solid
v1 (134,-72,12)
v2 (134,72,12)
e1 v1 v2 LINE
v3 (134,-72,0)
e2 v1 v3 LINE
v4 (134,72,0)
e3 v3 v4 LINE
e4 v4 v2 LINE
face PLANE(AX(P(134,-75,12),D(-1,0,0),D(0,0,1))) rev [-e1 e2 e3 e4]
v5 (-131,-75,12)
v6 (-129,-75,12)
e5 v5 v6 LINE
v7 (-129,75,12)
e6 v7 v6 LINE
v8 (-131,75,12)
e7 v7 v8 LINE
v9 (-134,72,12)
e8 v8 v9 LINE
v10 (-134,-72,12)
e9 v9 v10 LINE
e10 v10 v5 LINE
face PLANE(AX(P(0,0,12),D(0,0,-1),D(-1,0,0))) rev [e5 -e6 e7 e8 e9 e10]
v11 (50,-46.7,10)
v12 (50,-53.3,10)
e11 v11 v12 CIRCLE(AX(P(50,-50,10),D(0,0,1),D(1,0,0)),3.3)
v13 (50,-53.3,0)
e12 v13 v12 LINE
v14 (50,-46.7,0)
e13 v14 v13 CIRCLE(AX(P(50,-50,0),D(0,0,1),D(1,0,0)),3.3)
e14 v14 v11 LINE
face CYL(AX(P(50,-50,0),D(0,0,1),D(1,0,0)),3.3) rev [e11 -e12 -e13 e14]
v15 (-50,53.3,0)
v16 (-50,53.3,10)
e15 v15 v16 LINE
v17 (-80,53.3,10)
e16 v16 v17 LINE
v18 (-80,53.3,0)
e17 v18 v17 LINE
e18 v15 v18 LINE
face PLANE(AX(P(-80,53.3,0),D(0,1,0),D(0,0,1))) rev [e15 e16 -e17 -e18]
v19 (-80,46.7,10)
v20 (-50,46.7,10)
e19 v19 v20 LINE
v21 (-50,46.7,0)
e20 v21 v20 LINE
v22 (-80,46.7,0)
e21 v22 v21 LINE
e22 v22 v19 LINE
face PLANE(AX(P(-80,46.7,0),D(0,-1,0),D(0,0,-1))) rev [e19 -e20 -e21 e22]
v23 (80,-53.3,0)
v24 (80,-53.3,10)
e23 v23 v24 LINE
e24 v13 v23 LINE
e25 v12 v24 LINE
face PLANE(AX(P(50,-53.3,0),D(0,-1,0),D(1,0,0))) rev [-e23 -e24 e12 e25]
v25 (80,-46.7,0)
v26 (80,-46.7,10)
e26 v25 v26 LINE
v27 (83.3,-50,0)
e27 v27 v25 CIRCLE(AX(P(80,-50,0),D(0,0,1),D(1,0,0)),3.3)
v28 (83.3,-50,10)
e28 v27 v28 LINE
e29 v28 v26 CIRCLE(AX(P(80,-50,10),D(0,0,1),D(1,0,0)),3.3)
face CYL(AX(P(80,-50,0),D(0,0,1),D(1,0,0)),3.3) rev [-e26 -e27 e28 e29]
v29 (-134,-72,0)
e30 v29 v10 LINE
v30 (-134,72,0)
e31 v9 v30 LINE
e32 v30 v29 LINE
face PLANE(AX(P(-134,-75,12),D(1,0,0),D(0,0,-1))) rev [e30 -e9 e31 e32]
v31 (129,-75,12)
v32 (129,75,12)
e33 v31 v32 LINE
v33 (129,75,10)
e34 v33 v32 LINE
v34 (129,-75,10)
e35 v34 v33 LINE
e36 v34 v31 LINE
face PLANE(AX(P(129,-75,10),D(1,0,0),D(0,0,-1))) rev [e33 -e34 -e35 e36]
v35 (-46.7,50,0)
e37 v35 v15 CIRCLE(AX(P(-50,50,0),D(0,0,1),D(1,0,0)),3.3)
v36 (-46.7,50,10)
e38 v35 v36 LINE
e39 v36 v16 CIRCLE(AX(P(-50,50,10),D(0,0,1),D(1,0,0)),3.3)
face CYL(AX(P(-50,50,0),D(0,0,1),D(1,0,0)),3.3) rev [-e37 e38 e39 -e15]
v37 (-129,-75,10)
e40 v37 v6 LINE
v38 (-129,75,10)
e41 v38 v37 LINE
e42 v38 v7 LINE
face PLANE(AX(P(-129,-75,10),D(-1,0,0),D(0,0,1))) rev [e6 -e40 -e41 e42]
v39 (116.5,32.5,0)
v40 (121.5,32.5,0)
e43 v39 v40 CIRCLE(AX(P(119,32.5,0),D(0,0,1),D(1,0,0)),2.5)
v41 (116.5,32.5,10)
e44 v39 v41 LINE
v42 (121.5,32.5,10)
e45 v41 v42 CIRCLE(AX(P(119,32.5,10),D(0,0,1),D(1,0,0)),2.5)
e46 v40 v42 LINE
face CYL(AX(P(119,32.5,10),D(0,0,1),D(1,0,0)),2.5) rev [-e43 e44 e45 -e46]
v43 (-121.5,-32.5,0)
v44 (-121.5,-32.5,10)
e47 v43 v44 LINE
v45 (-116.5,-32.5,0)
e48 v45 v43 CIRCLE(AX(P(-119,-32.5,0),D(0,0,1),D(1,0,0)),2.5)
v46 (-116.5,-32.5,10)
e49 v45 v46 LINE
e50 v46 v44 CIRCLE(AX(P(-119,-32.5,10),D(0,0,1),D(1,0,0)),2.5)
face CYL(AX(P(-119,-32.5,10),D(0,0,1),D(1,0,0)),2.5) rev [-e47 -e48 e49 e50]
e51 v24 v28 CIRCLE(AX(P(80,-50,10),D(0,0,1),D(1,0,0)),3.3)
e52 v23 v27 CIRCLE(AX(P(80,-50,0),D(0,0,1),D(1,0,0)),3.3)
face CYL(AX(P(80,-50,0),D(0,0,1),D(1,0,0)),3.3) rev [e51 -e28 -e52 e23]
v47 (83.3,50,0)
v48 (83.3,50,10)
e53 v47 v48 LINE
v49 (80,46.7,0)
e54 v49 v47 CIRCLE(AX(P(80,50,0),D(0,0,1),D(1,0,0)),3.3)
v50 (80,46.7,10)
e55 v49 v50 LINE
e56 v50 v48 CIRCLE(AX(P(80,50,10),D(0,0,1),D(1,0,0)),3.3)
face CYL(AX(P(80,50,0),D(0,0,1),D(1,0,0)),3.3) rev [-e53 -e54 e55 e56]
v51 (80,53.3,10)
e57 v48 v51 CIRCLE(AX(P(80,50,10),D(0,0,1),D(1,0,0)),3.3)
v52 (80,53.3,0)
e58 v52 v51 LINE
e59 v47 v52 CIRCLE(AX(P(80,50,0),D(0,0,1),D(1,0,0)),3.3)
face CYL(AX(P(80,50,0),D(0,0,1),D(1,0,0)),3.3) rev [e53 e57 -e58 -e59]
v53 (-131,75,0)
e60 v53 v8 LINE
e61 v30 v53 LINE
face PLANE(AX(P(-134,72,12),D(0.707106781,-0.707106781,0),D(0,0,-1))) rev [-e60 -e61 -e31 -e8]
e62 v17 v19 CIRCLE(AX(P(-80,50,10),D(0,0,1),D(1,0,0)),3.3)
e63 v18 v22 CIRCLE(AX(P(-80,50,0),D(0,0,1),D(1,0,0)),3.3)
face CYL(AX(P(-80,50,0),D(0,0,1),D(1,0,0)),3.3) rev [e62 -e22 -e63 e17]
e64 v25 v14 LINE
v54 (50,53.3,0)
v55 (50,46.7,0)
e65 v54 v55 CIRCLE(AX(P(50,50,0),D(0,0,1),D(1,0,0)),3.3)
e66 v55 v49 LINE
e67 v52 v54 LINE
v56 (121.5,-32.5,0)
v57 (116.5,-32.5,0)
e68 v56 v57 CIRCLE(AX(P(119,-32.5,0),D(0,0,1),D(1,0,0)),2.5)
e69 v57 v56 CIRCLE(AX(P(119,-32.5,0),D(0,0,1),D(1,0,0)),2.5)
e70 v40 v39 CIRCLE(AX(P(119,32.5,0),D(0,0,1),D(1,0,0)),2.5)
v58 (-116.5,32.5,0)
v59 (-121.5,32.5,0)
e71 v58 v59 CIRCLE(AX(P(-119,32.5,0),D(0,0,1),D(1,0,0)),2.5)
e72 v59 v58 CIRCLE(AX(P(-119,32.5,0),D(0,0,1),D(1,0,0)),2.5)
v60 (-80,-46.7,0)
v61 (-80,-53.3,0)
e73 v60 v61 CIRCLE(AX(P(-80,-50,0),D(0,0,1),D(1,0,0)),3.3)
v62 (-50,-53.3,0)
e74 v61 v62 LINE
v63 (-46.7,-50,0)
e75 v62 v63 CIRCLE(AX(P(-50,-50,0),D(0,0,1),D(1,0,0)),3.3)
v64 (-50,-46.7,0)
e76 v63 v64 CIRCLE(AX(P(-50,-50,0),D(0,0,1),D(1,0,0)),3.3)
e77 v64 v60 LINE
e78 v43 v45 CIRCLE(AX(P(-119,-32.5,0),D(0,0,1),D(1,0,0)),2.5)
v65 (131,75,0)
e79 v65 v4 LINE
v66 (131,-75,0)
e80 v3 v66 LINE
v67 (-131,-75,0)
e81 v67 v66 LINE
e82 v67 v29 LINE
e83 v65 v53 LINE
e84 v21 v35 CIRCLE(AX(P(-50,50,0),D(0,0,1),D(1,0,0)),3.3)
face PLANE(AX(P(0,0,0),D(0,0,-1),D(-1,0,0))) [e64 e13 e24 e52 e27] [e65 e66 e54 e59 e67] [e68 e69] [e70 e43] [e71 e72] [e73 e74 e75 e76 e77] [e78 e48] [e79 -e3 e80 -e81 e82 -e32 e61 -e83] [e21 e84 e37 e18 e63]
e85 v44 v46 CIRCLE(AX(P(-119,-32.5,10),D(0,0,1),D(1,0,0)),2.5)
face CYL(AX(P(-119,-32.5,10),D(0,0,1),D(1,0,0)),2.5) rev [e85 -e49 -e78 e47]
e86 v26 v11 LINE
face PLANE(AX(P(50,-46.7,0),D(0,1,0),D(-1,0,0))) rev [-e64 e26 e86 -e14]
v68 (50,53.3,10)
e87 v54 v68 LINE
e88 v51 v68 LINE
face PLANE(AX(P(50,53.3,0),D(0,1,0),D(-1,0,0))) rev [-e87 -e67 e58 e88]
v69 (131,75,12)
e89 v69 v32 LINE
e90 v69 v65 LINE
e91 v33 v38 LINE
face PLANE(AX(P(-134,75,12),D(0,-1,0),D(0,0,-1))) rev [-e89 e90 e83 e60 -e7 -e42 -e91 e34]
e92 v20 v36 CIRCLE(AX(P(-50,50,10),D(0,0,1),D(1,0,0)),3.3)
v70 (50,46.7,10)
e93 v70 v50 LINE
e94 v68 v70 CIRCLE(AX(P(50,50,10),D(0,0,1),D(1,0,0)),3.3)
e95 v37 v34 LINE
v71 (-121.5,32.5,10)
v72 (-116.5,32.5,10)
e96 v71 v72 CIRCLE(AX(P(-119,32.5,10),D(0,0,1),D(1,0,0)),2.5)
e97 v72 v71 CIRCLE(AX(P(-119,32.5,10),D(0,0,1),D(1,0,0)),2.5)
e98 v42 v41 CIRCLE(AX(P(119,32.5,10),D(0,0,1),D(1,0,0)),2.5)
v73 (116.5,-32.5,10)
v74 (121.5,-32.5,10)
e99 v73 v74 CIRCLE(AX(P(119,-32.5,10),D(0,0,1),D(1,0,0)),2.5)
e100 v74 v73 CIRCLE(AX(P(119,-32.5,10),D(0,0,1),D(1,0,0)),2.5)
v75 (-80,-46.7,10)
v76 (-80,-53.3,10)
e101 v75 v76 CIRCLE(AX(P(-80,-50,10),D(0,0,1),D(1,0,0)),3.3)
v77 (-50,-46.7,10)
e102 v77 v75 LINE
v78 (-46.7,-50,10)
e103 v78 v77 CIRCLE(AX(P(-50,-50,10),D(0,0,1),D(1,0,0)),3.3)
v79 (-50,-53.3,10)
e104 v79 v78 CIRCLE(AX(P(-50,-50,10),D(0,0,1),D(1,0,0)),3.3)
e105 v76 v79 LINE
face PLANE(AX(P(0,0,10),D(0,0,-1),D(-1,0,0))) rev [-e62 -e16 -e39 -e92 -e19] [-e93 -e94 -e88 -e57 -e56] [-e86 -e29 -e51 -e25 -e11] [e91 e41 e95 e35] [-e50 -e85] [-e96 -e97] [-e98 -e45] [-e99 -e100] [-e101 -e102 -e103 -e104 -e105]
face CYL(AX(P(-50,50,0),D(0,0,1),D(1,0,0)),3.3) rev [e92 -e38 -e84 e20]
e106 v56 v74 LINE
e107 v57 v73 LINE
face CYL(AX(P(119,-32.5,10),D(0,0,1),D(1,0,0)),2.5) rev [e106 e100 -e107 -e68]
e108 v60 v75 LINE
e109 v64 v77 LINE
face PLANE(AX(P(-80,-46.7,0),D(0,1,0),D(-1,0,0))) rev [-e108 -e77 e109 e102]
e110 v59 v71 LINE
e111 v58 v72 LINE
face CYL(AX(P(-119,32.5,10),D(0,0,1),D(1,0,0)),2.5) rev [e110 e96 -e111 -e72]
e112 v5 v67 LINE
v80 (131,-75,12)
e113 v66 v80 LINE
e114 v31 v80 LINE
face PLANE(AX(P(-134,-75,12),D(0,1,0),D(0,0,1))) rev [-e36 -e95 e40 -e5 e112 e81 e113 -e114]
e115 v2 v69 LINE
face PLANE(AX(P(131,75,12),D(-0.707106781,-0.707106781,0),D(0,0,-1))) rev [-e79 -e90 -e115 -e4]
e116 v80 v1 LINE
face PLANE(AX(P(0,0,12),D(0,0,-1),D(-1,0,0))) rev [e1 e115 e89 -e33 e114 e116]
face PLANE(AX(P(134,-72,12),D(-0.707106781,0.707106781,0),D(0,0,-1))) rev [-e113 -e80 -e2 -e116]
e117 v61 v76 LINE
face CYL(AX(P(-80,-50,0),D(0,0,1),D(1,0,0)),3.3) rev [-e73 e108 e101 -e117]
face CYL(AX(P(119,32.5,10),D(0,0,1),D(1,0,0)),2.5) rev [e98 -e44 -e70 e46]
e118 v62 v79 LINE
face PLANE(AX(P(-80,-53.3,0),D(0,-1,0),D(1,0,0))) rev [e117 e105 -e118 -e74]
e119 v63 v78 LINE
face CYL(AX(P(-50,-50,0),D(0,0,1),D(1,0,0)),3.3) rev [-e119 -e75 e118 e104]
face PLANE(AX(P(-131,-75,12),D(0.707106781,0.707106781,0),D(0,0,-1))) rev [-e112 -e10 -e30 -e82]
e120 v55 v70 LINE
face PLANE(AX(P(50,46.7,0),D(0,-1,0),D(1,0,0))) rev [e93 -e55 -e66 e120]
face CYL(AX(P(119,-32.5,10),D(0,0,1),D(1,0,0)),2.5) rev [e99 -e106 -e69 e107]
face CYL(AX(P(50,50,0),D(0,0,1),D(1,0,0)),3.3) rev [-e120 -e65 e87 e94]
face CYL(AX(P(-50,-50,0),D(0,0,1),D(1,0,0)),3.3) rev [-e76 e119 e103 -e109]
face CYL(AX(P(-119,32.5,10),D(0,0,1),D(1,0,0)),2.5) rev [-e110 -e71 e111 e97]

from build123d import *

# Parameters (mm, degrees)
SKETCH_1_W          = 268
SKETCH_1_H          = 150
EXTRUDE_1_DEPTH     = 12
SKETCH_2_W          = 258
SKETCH_2_H          = 150
CUT_EXTRUDE_1_DEPTH = 2
CUT_EXTRUDE_2_DEPTH = 154.886321679
HOLE_WIZARD_M6_1_D  = 5
CHAMFER_1_SIZE      = 3


with BuildPart() as part:
    # 草图1 → 凸台-拉伸1 (new body)
    with BuildSketch(Plane.XY):
        Rectangle(SKETCH_1_W, SKETCH_1_H)
    extrude(amount=EXTRUDE_1_DEPTH)

    # 草图2 → 切除-拉伸1 (cut)
    with BuildSketch(Plane.XY.offset(12)):
        Rectangle(SKETCH_2_W, SKETCH_2_H)
    extrude(amount=-CUT_EXTRUDE_1_DEPTH, mode=Mode.SUBTRACT)

    # 草图3 → 切除-拉伸2 (cut, through all)
    with BuildSketch(Plane.XY.offset(10)):
        with BuildLine():
            Line((-80, 53.3), (-50, 53.3))
            ThreePointArc((-50, 53.3), (-46.7, 50), (-50, 46.7))
            Line((-50, 46.7), (-80, 46.7))
            ThreePointArc((-80, 46.7), (-83.3, 50), (-80, 53.3))
        make_face()
        with BuildLine():
            Line((50, 53.3), (80, 53.3))
            ThreePointArc((80, 53.3), (83.3, 50), (80, 46.7))
            Line((80, 46.7), (50, 46.7))
            ThreePointArc((50, 46.7), (46.7, 50), (50, 53.3))
        make_face()
        with BuildLine():
            Line((-80, -46.7), (-50, -46.7))
            ThreePointArc((-50, -46.7), (-46.7, -50), (-50, -53.3))
            Line((-50, -53.3), (-80, -53.3))
            ThreePointArc((-80, -53.3), (-83.3, -50), (-80, -46.7))
        make_face()
        with BuildLine():
            Line((50, -46.7), (80, -46.7))
            ThreePointArc((80, -46.7), (83.3, -50), (80, -53.3))
            Line((80, -53.3), (50, -53.3))
            ThreePointArc((50, -53.3), (46.7, -50), (50, -46.7))
        make_face()
    extrude(amount=-CUT_EXTRUDE_2_DEPTH, mode=Mode.SUBTRACT)

    # M6 螺纹孔1 (through all)
    with Locations(Plane.XY.offset(10)):
        with Locations((-119, 32.5), (-119, -32.5), (119, 32.5), (119, -32.5)):
            Hole(HOLE_WIZARD_M6_1_D / 2)

    # 倒角1
    chamfer_1_edges = [part.edges().sort_by_distance(p)[0] for p in [
        (134, -75, 6),
        (-134, -75, 6),
        (-134, 75, 6),
        (134, 75, 6),
    ]]
    chamfer(chamfer_1_edges, length=CHAMFER_1_SIZE)


solid = part.part
